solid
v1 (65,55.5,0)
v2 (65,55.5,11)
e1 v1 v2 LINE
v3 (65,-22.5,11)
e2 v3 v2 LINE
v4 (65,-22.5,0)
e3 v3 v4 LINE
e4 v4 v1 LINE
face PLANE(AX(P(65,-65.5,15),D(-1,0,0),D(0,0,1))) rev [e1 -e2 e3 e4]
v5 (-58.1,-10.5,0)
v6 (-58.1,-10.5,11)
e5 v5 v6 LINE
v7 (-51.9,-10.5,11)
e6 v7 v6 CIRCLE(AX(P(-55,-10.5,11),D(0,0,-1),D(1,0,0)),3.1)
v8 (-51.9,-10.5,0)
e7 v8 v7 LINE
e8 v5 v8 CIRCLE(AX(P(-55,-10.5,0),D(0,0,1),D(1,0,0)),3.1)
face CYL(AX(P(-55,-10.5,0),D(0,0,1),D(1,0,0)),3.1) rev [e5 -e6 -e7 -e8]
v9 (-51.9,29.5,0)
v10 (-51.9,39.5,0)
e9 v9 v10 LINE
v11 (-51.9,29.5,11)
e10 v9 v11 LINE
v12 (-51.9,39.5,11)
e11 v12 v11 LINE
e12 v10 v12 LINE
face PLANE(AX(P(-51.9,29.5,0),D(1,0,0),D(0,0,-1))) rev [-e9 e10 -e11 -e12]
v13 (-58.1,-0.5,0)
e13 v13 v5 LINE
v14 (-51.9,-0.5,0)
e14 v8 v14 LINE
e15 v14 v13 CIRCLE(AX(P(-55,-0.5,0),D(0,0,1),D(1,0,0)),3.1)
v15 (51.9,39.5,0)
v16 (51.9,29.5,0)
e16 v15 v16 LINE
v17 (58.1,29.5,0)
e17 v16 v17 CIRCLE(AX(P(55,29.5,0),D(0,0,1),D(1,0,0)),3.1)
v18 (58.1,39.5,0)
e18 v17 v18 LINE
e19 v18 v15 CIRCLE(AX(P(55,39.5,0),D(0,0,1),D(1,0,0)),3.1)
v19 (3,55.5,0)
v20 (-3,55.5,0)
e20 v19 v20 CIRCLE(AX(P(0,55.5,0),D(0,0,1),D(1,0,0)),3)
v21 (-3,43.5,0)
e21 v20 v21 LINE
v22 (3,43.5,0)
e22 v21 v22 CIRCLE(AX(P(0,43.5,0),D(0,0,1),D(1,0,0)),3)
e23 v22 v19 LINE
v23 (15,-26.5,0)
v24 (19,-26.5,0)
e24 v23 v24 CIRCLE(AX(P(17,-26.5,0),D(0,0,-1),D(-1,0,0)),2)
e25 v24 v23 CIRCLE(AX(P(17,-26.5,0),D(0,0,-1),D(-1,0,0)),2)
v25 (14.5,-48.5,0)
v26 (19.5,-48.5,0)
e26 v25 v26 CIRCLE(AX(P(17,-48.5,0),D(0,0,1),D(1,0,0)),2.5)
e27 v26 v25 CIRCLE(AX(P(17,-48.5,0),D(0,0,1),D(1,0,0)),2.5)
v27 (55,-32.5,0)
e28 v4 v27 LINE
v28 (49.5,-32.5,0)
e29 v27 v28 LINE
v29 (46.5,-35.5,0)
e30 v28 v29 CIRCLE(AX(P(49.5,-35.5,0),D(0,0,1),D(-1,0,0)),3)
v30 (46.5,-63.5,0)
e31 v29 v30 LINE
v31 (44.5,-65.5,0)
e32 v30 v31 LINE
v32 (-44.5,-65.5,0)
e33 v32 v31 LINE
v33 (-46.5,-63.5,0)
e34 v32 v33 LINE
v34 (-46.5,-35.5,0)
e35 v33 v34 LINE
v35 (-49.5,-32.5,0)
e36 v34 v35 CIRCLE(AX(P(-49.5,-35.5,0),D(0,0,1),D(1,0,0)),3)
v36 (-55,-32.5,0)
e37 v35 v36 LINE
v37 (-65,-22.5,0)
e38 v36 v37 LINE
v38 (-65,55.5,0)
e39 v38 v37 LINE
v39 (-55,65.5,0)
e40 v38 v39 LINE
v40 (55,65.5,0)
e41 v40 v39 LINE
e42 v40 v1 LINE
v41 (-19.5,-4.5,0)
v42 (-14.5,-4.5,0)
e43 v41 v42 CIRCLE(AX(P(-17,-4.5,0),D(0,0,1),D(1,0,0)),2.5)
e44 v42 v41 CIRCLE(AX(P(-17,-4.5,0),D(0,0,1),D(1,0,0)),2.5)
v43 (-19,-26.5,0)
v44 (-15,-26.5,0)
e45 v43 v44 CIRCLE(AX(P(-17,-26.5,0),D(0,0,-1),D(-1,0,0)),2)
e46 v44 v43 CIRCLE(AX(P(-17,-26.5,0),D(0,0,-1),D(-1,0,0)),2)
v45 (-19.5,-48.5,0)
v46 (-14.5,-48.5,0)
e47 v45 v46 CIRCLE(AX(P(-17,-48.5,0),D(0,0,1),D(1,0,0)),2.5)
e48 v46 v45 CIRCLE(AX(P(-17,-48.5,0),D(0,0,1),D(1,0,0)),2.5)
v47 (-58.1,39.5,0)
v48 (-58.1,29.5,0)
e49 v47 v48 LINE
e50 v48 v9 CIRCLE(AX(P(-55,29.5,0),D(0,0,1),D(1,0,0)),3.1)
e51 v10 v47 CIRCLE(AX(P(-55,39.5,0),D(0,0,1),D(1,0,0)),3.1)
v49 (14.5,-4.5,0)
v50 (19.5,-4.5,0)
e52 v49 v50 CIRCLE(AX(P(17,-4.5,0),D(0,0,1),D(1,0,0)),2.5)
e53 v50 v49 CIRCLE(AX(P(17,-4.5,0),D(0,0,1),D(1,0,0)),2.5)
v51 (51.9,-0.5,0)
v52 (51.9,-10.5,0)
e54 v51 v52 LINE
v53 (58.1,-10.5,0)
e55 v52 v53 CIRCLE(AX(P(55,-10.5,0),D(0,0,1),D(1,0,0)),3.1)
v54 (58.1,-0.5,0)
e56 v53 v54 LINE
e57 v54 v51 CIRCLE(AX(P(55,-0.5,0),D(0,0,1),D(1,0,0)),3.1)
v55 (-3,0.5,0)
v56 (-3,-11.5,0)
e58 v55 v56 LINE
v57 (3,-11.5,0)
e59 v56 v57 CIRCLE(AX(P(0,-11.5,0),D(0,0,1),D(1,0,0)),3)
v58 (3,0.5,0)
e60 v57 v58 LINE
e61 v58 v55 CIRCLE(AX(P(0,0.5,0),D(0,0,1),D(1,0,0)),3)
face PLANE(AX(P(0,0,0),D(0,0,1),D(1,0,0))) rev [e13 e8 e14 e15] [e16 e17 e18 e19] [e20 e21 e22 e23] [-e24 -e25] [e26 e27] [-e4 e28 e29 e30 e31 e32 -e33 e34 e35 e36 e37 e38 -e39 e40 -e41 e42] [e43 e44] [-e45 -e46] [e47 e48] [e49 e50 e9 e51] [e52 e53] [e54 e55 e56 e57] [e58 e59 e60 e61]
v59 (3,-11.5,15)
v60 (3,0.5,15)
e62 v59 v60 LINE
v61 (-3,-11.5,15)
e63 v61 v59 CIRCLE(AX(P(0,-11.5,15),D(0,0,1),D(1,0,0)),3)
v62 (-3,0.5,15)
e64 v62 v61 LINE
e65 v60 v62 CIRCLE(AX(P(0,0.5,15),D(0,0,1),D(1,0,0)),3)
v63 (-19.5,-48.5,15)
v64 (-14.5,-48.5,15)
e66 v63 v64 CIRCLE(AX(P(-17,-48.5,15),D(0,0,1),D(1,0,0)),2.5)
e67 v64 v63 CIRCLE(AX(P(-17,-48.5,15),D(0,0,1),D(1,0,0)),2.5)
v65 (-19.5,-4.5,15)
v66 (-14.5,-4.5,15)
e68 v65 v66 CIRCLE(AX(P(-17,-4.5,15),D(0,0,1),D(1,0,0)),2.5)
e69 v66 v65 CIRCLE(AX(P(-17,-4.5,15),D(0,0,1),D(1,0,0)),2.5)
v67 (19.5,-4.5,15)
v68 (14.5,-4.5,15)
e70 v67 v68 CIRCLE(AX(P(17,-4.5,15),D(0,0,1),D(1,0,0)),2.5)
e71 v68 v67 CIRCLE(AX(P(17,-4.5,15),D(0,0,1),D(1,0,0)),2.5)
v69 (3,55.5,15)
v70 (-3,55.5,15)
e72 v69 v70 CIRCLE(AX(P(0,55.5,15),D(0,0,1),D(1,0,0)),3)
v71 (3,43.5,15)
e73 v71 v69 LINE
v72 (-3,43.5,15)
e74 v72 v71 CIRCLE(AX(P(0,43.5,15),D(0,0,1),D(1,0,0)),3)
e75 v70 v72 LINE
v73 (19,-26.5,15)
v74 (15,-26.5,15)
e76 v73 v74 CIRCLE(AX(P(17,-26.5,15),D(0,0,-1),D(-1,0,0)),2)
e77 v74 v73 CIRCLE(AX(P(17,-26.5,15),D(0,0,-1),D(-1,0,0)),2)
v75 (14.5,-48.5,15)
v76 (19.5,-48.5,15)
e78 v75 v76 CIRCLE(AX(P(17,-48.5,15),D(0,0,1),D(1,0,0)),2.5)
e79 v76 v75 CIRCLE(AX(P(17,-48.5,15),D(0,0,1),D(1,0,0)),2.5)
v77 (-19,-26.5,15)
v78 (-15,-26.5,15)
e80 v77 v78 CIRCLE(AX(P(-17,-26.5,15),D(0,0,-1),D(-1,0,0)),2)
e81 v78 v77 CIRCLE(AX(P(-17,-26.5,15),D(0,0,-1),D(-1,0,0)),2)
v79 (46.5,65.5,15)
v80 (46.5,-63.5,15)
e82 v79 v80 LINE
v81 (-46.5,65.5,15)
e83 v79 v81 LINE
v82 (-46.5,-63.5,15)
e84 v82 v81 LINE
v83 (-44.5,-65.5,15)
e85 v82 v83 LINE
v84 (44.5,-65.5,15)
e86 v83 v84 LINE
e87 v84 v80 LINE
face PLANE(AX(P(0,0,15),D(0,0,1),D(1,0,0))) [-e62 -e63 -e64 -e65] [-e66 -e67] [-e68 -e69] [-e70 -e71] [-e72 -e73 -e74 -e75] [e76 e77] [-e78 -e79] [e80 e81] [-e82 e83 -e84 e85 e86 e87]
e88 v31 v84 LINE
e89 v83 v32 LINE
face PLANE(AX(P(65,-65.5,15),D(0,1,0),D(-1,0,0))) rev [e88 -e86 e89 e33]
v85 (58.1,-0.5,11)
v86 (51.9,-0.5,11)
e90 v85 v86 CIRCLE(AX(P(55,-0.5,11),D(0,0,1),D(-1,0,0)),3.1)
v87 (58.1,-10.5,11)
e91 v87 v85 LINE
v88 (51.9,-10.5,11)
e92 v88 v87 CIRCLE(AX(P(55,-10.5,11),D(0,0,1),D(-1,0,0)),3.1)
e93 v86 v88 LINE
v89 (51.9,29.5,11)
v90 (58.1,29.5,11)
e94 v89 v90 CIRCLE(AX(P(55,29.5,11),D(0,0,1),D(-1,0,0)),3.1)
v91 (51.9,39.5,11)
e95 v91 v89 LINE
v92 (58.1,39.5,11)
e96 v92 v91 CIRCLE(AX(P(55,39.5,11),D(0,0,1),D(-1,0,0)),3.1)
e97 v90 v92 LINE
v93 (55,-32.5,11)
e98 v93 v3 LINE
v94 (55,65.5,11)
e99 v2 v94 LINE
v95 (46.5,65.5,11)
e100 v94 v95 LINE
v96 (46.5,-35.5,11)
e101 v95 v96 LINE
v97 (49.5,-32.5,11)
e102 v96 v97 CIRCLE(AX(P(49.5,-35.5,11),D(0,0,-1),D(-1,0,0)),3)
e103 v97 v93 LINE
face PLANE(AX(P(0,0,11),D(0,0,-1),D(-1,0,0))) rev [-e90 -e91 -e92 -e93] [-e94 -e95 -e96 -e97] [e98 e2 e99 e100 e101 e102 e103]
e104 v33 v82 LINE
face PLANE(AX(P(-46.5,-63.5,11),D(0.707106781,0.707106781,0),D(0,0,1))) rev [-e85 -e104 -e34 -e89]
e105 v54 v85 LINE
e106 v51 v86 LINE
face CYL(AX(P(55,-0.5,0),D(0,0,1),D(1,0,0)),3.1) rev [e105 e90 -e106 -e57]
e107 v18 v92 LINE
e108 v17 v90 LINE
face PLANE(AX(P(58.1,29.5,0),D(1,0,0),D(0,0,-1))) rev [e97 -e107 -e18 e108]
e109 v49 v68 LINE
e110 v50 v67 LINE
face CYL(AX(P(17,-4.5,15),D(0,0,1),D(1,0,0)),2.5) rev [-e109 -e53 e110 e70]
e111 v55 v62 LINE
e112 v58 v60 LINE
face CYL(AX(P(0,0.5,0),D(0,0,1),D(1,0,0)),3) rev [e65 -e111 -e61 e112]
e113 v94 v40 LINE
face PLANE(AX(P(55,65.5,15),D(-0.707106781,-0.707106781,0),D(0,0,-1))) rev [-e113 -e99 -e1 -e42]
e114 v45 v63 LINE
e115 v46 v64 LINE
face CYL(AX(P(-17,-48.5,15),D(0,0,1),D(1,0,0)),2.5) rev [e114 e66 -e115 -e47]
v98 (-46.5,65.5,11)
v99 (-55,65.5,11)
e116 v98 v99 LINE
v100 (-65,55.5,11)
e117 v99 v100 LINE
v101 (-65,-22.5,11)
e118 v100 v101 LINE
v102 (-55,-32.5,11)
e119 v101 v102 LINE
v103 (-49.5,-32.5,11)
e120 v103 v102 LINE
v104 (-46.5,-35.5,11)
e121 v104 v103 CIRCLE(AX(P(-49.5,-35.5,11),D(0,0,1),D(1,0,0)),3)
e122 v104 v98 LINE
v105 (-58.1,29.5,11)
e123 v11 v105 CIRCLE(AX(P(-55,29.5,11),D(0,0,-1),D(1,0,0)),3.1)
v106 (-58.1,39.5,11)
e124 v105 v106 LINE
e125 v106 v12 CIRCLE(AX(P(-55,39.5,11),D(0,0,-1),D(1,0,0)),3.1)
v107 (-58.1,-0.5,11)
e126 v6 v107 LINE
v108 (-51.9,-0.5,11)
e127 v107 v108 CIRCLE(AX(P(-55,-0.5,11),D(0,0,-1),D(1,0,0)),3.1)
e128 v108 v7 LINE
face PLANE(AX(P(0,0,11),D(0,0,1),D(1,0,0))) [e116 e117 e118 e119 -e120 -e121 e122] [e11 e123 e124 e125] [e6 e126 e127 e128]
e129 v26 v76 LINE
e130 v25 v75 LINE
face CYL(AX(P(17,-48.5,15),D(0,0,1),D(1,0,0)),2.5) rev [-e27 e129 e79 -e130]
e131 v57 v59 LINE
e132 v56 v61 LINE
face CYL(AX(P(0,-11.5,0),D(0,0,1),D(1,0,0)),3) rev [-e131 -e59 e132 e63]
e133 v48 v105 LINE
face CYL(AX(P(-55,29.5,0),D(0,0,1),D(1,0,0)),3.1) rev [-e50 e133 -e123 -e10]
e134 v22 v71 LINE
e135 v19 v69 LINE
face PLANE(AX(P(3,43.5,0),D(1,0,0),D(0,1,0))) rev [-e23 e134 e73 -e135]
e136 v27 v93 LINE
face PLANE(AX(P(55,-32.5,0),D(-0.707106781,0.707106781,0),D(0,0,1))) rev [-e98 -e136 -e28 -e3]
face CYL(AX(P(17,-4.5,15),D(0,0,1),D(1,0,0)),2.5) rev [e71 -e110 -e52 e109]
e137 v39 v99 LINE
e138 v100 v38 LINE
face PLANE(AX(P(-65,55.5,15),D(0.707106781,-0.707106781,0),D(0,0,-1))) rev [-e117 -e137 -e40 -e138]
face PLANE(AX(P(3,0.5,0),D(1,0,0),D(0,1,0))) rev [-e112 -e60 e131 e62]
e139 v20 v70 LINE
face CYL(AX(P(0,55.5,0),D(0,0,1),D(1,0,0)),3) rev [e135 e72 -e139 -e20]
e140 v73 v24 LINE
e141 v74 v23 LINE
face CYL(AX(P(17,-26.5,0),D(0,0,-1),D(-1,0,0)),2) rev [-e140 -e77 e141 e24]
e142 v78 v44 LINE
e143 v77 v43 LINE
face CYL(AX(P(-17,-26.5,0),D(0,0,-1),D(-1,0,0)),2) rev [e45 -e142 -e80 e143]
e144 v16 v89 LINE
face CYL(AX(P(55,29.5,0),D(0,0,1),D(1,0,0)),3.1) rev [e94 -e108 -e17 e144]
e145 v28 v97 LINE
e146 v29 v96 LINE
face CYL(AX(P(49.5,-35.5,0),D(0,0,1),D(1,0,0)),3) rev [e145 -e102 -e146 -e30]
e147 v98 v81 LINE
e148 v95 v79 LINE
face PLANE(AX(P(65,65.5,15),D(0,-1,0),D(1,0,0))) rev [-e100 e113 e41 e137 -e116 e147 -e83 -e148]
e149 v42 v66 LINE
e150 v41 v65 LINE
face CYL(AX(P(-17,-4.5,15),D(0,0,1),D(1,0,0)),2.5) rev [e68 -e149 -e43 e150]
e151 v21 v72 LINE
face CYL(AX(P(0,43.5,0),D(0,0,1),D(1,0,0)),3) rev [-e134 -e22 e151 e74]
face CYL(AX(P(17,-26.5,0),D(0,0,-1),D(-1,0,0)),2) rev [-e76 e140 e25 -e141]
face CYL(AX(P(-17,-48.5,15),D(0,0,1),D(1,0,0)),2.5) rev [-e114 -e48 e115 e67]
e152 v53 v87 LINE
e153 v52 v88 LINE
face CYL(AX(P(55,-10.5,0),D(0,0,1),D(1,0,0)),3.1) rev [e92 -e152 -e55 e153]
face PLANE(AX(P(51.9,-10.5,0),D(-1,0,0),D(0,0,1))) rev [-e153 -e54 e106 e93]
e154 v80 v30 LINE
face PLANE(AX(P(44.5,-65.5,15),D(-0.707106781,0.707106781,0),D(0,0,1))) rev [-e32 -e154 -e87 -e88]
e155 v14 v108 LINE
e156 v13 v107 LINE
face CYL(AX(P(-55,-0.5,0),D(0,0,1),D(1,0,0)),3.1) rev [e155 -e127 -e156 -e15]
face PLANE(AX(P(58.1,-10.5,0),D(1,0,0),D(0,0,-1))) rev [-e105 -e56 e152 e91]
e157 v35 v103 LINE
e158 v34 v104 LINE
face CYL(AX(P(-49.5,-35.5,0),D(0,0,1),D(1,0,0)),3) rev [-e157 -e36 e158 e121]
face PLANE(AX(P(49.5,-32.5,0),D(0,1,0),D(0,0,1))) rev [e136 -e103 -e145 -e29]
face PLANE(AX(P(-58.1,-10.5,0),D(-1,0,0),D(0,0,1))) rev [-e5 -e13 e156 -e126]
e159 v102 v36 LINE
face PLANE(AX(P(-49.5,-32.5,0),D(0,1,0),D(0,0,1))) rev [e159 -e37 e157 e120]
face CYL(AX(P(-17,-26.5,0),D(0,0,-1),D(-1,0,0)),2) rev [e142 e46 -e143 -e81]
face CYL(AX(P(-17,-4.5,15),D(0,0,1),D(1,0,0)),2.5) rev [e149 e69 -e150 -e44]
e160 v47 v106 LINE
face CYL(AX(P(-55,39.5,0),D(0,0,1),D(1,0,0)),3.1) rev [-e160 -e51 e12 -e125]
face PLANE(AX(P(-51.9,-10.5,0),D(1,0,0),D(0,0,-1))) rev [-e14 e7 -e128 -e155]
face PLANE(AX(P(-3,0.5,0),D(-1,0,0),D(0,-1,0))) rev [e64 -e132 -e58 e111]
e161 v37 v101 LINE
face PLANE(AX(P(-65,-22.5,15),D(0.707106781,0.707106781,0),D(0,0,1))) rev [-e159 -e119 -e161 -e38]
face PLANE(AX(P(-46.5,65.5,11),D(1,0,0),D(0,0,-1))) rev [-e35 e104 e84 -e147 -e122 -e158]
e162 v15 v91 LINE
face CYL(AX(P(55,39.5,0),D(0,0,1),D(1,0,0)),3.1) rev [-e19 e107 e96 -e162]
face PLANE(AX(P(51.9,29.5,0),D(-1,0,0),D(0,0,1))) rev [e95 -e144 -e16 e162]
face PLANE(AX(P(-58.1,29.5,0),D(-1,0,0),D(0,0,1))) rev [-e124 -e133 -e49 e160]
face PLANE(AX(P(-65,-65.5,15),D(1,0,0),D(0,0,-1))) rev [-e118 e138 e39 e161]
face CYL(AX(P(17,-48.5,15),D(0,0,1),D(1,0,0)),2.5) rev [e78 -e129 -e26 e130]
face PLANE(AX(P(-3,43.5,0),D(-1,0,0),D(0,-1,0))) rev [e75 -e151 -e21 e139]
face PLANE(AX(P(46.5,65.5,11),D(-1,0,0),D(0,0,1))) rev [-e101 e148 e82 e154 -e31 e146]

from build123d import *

# Parameters (mm, degrees)
SKETCH1_W               = 130
SKETCH1_H               = 131
EXTRUDE1_DEPTH          = 15
M6_TAPPED_HOLE1_D       = 5
EXTRUDE2_DEPTH          = 94.489304201
SKETCH5_W               = 18.5
SKETCH5_H               = 131
EXTRUDE3_DEPTH          = 4
CHAMFER1_SIZE           = 10
F_4_0_MM_DOWEL_HOLES1_D = 4
EXTRUDE4_DEPTH          = 94.489304201
EXTRUDE5_DEPTH          = 94.489304201
CHAMFER2_SIZE           = 10
CHAMFER3_SIZE           = 2


with BuildPart() as part:
    # Sketch1 → Extrude1 (new body)
    with BuildSketch(Plane.XY):
        Rectangle(SKETCH1_W, SKETCH1_H)
    extrude(amount=EXTRUDE1_DEPTH)

    # M6 Tapped Hole1 (through all)
    with Locations(Plane.XY.offset(15)):
        with Locations((17, -48.5), (-17, -48.5), (-17, -4.5), (17, -4.5)):
            Hole(M6_TAPPED_HOLE1_D / 2)

    # Sketch4 → Extrude2 (cut, through all)
    with BuildSketch(Plane.XY.offset(15)):
        with BuildLine():
            Line((-58.1, -10.5), (-58.1, -0.5))
            ThreePointArc((-58.1, -0.5), (-55, 2.6), (-51.9, -0.5))
            Line((-51.9, -0.5), (-51.9, -10.5))
            ThreePointArc((-51.9, -10.5), (-55, -13.6), (-58.1, -10.5))
        make_face()
        with BuildLine():
            Line((-58.1, 29.5), (-58.1, 39.5))
            ThreePointArc((-58.1, 39.5), (-55, 42.6), (-51.9, 39.5))
            Line((-51.9, 39.5), (-51.9, 29.5))
            ThreePointArc((-51.9, 29.5), (-55, 26.4), (-58.1, 29.5))
        make_face()
        with BuildLine():
            Line((51.9, -10.5), (51.9, -0.5))
            ThreePointArc((51.9, -0.5), (55, 2.6), (58.1, -0.5))
            Line((58.1, -0.5), (58.1, -10.5))
            ThreePointArc((58.1, -10.5), (55, -13.6), (51.9, -10.5))
        make_face()
        with BuildLine():
            Line((51.9, 29.5), (51.9, 39.5))
            ThreePointArc((51.9, 39.5), (55, 42.6), (58.1, 39.5))
            Line((58.1, 39.5), (58.1, 29.5))
            ThreePointArc((58.1, 29.5), (55, 26.4), (51.9, 29.5))
        make_face()
    extrude(amount=-EXTRUDE2_DEPTH, mode=Mode.SUBTRACT)

    # Sketch5 → Extrude3 (cut)
    with BuildSketch(Plane.XY.offset(15)):
        with Locations((-55.75, 0)):
            Rectangle(SKETCH5_W, SKETCH5_H)
        with Locations((55.75, 0)):
            Rectangle(SKETCH5_W, SKETCH5_H)
    extrude(amount=-EXTRUDE3_DEPTH, mode=Mode.SUBTRACT)

    # Chamfer1
    chamfer1_edges = [part.edges().sort_by_distance(p)[0] for p in [
        (-65, 65.5, 5.5),
        (65, 65.5, 5.5),
    ]]
    chamfer(chamfer1_edges, length=CHAMFER1_SIZE)

    # Ø4.0 mm Dowel Holes1 (through all)
    with Locations(Plane(origin=(0, 0, 0), x_dir=(-1, 0, 0), z_dir=(0, 0, -1))):
        with Locations((-17, -26.5), (17, -26.5)):
            Hole(F_4_0_MM_DOWEL_HOLES1_D / 2)

    # Sketch8 → Extrude4 (cut, through all)
    with BuildSketch(Plane.XY.offset(15)):
        with BuildLine():
            Line((-3, 43.5), (-3, 55.5))
            ThreePointArc((-3, 55.5), (0, 58.5), (3, 55.5))
            Line((3, 55.5), (3, 43.5))
            ThreePointArc((3, 43.5), (0, 40.5), (-3, 43.5))
        make_face()
        with BuildLine():
            Line((3, 0.5), (3, -11.5))
            ThreePointArc((3, -11.5), (0, -14.5), (-3, -11.5))
            Line((-3, -11.5), (-3, 0.5))
            ThreePointArc((-3, 0.5), (0, 3.5), (3, 0.5))
        make_face()
    extrude(amount=-EXTRUDE4_DEPTH, mode=Mode.SUBTRACT)

    # Sketch9 → Extrude5 (cut, through all)
    with BuildSketch(Plane.XY.offset(15)):
        with BuildLine():
            Line((-46.5, -65.5), (-65, -65.5))
            Line((-65, -65.5), (-65, -32.5))
            Line((-65, -32.5), (-49.5, -32.5))
            ThreePointArc((-49.5, -32.5), (-47.378679656, -33.378679656), (-46.5, -35.5))
            Line((-46.5, -35.5), (-46.5, -65.5))
        make_face()
        with BuildLine():
            Line((46.5, -65.5), (65, -65.5))
            Line((65, -65.5), (65, -32.5))
            Line((65, -32.5), (49.5, -32.5))
            ThreePointArc((49.5, -32.5), (47.378679656, -33.378679656), (46.5, -35.5))
            Line((46.5, -35.5), (46.5, -65.5))
        make_face()
    extrude(amount=-EXTRUDE5_DEPTH, mode=Mode.SUBTRACT)

    # Chamfer2
    chamfer2_edges = [part.edges().sort_by_distance(p)[0] for p in [
        (-65, -32.5, 5.5),
        (65, -32.5, 5.5),
    ]]
    chamfer(chamfer2_edges, length=CHAMFER2_SIZE)

    # Chamfer3
    chamfer3_edges = [part.edges().sort_by_distance(p)[0] for p in [
        (-46.5, -65.5, 7.5),
        (46.5, -65.5, 7.5),
    ]]
    chamfer(chamfer3_edges, length=CHAMFER3_SIZE)


solid = part.part
